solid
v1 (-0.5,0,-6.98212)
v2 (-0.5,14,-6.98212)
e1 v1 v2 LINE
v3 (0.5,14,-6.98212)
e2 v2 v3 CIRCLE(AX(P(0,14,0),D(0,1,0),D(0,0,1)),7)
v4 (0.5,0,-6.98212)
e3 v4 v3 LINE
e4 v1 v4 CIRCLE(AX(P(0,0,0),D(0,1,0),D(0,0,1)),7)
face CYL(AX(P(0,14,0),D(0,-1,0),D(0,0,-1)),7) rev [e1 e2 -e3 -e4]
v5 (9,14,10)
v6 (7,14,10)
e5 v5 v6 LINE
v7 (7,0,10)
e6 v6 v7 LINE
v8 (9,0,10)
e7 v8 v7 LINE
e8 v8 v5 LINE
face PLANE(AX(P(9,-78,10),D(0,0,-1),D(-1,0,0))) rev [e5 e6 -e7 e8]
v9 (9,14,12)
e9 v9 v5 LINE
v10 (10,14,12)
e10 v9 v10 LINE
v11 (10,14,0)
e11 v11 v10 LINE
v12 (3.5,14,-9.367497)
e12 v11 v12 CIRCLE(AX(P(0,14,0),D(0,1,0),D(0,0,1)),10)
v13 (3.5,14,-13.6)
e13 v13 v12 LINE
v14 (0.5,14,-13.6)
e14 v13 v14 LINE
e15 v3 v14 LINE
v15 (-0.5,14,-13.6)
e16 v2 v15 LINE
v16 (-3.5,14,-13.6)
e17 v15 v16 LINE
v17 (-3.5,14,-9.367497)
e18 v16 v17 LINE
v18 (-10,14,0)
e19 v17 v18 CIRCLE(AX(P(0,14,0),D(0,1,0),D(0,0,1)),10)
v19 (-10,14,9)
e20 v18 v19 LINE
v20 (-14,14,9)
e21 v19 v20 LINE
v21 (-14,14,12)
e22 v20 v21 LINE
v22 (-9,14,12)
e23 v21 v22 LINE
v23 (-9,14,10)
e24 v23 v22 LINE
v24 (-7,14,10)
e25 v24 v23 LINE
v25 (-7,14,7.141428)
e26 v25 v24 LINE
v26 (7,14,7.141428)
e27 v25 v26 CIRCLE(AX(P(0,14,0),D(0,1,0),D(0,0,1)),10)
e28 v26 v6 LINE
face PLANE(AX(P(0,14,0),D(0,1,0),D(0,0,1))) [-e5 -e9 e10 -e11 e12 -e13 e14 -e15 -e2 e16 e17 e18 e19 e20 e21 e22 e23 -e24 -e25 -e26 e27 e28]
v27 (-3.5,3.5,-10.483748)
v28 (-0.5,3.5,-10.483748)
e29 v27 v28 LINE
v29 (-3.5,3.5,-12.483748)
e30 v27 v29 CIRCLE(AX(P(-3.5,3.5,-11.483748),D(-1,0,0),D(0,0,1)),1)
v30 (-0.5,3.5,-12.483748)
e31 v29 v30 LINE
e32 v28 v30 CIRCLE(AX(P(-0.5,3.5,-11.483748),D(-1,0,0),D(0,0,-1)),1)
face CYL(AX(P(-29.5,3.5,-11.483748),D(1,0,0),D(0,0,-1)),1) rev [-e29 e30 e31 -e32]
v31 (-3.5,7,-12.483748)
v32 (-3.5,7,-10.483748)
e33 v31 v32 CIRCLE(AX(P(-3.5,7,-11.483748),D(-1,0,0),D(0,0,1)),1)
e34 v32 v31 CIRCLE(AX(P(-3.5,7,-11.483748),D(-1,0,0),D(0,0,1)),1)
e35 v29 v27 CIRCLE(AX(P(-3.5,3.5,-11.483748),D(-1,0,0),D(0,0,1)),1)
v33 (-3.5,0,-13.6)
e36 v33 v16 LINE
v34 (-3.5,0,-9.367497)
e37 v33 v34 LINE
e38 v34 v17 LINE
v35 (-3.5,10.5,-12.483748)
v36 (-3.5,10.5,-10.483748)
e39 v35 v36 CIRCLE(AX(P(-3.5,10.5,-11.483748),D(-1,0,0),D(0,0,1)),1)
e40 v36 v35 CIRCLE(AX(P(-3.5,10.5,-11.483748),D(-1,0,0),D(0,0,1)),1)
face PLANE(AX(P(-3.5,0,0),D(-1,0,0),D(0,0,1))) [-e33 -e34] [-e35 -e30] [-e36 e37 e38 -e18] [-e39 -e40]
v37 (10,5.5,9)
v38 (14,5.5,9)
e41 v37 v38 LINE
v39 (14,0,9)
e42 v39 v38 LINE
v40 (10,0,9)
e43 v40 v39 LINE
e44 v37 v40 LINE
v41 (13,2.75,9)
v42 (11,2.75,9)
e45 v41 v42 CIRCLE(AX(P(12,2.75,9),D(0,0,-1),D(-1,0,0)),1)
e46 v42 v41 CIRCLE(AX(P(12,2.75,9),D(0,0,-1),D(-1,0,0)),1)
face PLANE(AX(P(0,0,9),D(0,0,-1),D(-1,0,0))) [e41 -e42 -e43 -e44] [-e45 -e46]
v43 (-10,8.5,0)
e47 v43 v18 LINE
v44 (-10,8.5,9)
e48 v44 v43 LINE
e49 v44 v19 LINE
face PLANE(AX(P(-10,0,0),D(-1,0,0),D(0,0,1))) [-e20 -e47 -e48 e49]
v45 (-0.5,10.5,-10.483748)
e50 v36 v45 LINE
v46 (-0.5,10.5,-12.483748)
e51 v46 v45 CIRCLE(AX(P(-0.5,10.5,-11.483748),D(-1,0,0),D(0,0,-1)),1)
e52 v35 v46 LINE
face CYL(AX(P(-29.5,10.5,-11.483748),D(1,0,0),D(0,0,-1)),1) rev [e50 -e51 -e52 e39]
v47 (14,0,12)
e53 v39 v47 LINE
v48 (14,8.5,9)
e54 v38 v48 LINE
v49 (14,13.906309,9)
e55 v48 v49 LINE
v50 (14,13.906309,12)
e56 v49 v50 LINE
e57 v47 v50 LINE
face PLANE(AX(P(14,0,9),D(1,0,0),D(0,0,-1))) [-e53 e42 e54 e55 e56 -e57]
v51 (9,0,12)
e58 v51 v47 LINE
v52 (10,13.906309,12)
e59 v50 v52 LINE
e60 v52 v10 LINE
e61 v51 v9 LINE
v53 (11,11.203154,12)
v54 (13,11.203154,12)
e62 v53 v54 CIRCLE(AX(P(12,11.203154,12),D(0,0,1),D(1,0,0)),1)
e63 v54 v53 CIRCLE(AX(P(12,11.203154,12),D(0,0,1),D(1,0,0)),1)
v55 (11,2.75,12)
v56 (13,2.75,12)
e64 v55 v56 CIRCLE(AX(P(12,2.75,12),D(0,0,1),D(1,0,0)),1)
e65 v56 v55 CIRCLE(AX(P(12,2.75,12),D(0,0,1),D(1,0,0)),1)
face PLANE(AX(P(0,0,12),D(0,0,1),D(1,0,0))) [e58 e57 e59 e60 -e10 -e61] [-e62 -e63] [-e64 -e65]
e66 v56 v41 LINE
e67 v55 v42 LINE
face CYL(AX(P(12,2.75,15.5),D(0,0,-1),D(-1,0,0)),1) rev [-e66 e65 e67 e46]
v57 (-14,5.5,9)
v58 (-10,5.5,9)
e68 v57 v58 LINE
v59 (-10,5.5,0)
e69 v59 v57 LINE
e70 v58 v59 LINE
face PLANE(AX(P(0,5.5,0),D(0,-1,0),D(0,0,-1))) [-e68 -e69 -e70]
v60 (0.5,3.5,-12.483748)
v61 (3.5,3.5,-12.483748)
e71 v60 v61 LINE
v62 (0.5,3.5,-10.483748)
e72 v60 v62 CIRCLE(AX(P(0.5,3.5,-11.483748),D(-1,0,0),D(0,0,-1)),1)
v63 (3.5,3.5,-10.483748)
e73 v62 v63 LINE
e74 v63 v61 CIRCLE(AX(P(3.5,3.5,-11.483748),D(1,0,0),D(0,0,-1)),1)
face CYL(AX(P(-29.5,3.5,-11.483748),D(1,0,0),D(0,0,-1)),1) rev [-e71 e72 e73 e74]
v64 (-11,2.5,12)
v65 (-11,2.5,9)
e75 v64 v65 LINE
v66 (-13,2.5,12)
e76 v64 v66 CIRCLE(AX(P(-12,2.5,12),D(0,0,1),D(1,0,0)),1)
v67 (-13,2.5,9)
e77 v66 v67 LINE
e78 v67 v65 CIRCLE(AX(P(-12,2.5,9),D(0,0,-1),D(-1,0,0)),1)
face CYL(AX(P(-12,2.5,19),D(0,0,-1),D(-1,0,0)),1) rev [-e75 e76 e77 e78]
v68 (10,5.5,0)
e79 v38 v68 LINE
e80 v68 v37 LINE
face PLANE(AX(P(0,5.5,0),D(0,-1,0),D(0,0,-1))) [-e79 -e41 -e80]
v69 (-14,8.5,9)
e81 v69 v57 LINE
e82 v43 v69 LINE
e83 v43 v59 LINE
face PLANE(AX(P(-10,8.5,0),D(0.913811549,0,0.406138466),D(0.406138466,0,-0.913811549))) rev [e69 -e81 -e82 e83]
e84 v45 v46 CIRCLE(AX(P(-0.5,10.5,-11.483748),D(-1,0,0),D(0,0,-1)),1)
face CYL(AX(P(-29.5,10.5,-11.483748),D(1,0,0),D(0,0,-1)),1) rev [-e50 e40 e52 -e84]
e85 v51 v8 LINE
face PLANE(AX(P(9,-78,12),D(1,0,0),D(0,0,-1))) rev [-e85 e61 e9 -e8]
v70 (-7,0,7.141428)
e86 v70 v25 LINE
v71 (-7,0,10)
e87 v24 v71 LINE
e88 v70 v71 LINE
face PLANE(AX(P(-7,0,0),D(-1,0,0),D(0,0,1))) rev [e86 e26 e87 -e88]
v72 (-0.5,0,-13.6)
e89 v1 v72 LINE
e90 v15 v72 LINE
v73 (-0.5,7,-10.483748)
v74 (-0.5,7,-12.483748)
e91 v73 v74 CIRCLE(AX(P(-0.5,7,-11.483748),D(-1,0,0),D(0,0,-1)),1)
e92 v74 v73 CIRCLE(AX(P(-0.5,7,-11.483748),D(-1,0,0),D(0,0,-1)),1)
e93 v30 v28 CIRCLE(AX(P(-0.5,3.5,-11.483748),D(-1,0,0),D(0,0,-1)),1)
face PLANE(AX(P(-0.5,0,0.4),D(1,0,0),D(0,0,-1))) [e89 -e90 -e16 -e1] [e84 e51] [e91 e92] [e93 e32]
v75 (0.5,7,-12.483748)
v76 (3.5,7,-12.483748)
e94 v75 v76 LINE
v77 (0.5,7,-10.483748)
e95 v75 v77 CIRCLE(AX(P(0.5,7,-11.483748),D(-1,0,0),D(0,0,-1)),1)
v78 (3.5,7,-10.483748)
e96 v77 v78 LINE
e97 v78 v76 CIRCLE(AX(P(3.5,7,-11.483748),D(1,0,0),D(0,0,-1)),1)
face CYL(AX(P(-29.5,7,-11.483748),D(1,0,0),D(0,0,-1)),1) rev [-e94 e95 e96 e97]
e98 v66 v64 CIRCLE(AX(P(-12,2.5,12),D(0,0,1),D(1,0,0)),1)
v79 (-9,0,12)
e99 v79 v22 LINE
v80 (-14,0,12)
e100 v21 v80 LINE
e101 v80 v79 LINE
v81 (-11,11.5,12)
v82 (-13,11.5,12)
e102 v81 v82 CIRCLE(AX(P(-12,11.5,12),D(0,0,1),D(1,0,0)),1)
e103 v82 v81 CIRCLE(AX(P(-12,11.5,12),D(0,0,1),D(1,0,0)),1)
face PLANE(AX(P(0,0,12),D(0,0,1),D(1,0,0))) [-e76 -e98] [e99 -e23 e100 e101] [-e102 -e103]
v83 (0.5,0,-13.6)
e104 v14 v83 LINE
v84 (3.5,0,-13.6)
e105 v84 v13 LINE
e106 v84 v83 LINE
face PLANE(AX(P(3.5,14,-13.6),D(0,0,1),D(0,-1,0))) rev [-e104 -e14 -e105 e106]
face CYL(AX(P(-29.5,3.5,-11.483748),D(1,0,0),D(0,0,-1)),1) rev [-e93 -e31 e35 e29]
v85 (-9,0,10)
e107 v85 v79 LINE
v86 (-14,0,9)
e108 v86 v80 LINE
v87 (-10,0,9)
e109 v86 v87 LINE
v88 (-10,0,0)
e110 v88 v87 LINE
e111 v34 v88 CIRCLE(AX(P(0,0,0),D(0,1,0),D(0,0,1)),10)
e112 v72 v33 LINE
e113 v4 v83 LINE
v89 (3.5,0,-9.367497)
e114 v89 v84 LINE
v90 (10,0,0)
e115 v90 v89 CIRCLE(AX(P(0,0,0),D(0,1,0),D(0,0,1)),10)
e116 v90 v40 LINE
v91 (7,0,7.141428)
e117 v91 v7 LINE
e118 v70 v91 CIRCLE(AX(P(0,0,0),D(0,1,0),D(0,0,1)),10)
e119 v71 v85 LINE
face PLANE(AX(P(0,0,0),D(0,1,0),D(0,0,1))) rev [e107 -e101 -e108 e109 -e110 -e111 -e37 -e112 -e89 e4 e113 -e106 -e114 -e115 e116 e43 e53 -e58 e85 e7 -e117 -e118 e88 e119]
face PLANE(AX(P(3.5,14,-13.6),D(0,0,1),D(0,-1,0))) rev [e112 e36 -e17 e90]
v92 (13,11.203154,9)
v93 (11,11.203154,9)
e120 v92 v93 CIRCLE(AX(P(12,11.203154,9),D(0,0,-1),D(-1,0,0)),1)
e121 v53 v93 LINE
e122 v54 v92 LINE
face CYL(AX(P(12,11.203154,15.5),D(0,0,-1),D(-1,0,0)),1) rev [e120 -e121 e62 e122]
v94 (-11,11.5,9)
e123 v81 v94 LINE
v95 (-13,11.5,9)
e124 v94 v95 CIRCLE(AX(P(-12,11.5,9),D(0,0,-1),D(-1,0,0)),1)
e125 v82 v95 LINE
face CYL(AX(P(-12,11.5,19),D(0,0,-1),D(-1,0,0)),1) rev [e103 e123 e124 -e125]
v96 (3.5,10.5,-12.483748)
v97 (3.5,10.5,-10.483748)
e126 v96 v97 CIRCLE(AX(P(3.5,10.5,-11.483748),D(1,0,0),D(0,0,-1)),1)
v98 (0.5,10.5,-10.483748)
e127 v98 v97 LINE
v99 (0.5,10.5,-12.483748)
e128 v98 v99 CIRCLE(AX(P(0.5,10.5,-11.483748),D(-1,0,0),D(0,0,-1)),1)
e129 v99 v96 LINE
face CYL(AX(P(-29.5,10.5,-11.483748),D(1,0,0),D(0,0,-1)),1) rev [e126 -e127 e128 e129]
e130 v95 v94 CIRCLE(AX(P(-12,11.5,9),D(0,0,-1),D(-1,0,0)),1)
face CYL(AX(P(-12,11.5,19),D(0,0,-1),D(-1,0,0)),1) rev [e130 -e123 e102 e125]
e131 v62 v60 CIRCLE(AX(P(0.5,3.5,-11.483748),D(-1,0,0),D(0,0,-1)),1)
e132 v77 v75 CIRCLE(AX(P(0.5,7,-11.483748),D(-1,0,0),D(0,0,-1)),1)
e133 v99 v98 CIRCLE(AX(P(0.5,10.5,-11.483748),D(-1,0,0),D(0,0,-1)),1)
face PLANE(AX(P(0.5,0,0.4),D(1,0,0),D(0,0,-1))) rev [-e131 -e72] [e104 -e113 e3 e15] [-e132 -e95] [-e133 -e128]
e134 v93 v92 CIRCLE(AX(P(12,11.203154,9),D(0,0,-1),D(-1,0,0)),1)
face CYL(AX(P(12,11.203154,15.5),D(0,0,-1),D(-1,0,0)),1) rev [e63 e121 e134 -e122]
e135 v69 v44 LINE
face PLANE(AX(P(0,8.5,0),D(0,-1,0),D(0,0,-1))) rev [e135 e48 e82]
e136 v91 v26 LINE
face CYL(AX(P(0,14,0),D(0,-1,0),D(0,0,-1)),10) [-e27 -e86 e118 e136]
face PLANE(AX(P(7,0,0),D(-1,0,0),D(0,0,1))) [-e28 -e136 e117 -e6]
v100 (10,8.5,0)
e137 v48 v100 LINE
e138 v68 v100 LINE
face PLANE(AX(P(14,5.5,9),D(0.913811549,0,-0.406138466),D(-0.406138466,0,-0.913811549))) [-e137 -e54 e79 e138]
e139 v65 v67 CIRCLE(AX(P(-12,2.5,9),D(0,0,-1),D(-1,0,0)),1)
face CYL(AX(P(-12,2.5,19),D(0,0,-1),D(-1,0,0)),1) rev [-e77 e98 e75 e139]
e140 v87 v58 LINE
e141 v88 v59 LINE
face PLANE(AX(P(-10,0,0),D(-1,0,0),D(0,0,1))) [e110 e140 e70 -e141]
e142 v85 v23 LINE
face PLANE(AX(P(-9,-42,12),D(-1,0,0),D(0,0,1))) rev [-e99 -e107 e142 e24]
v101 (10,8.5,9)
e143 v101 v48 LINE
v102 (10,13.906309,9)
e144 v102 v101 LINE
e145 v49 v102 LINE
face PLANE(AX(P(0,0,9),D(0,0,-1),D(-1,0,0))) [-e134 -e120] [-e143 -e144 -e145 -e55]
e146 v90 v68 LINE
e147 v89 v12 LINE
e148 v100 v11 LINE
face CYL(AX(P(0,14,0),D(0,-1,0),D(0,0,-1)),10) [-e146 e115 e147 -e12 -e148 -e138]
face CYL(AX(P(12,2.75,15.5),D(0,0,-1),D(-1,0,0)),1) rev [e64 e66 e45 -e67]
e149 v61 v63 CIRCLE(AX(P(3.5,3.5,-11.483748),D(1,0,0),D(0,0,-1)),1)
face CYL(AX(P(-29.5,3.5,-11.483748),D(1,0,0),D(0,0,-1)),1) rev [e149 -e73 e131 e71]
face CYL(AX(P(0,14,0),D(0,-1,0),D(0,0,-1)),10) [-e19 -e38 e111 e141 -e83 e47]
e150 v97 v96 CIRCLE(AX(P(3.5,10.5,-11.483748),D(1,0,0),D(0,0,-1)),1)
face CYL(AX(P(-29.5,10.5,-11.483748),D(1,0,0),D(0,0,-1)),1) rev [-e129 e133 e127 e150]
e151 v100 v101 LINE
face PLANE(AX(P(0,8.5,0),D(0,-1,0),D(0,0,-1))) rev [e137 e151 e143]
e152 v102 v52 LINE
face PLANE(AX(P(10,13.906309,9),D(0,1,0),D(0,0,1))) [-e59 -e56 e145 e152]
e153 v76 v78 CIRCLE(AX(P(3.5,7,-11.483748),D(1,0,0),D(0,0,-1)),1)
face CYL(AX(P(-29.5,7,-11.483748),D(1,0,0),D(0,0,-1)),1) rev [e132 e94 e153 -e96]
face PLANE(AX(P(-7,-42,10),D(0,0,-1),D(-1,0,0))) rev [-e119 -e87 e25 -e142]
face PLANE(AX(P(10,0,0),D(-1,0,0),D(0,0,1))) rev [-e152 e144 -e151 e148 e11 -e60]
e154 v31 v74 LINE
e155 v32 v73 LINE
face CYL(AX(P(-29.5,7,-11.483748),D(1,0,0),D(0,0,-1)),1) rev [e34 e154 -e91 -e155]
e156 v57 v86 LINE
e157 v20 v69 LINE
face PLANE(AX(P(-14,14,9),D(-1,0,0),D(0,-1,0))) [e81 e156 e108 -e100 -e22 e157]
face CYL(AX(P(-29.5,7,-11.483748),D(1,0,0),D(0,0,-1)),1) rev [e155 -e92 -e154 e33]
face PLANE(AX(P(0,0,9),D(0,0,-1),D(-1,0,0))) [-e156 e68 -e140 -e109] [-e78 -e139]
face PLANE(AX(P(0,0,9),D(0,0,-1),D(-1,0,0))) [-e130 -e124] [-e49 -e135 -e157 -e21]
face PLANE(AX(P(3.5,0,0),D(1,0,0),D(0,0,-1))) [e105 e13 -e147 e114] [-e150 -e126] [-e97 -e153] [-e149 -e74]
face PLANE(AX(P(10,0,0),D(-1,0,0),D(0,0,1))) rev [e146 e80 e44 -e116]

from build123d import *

# Parameters (mm, degrees)
BASE_BLOCK_SKETCH_R              = 10
BASE_BLOCK_SKETCH_R_2            = 7
BASE_BLOCK_DEPTH                 = 14
CLAMP_START                      = -14
CLAMP_RING_DEPTH                 = 14
SIDE_RIB_SKETCH_W                = 3.6
SIDE_RIB_SKETCH_H                = 14
SIDE_RIB_DEPTH                   = 3.5
RIB_START                        = -14
RIB_INFILL_DEPTH                 = 14
MOUNTING_EAR_A_SKETCH_W          = 4
MOUNTING_EAR_A_SKETCH_H          = 13.906308923
MOUNTING_EAR_A_DEPTH             = 3
MOUNTING_EAR_B_SKETCH_W          = 4
MOUNTING_EAR_B_SKETCH_H          = 14
MOUNTING_EAR_B_DEPTH             = 3
CLAMP_SLIT_A_SKETCH_W            = 2
CLAMP_SLIT_A_SKETCH_H            = 2
CLAMP_SLIT_A_DEPTH               = 56
CLAMP_SLIT_B_SKETCH_W            = 2
CLAMP_SLIT_B_SKETCH_H            = 2
CLAMP_SLIT_B_DEPTH               = 92
TRIANGULAR_RELIEF_CUT_DEPTH      = 54
TRIANGULAR_RELIEF_CUT_DEPTH_BACK = 33
TRIANGULAR_RELIEF_SKETCH_R       = 1
RIB_GROOVE_SKETCH_W              = 0.5
RIB_GROOVE_SKETCH_H              = 14
RIB_GROOVE_CUT_DEPTH             = 14
EAR_A_GUSSET_DEPTH               = 1.5
EAR_A_HOLES_SKETCH_R             = 1
EAR_A_HOLES_2X_2_DEPTH           = 6.5
EAR_B_GUSSET_DEPTH               = 1.5
EAR_B_HOLES_SKETCH_R             = 1
EAR_B_HOLES_2X_2_DEPTH           = 10


with BuildPart() as part:
    # Base Block Sketch → Base Block (new body)
    with BuildSketch(Plane(origin=(0, 0, 0), x_dir=(1, 0, 0), z_dir=(0, 1, 0))):
        with Locations(Location((0, 0, 0), (0, 0, 270))):
            Circle(BASE_BLOCK_SKETCH_R)
        with Locations(Location((0, 0, 0), (0, 0, 270))):
            Circle(BASE_BLOCK_SKETCH_R_2, mode=Mode.SUBTRACT)
    extrude(amount=BASE_BLOCK_DEPTH)

    # Clamp Ring Sketch → Clamp Ring (add)
    with BuildSketch(Plane(origin=(0, 14, 0), x_dir=(1, 0, 0), z_dir=(0, 1, 0)).offset(CLAMP_START)):
        with BuildLine():
            Line((-7, -12), (-7, -7.141428429))
            ThreePointArc((-7, -7.141428429), (-9.219544457, -3.872983346), (-10, 0))
            Line((-10, 0), (-10, -12))
            Line((-10, -12), (-7, -12))
        make_face()
        with BuildLine():
            Line((10, -12), (10, 0))
            ThreePointArc((10, 0), (9.219544457, -3.872983346), (7, -7.141428429))
            Line((7, -7.141428429), (7, -12))
            Line((7, -12), (10, -12))
        make_face()
    extrude(amount=CLAMP_RING_DEPTH)



with BuildPart() as body_2:
    # Side Rib Sketch → Side Rib (new, symmetric)
    with BuildSketch(Plane(origin=(0, 0, 0), x_dir=(0, 0, -1), z_dir=(1, 0, 0))):
        with Locations((11.8, 7)):
            Rectangle(SIDE_RIB_SKETCH_W, SIDE_RIB_SKETCH_H)
    extrude(amount=SIDE_RIB_DEPTH, both=True)


with BuildPart() as part_1:
    add(part.part)

    add(body_2.part)  # Rib Infill merges body 2
    # Rib Infill Sketch → Rib Infill (add)
    with BuildSketch(Plane(origin=(0, 14, 0), x_dir=(1, 0, 0), z_dir=(0, 1, 0)).offset(RIB_START)):
        with BuildLine():
            Line((0, 10), (-3.5, 10))
            Line((-3.5, 10), (-3.5, 9.367496998))
            ThreePointArc((-3.5, 9.367496998), (-1.778346145, 9.840603893), (0, 10))
        make_face()
        with BuildLine():
            Line((3.5, 10), (0, 10))
            ThreePointArc((0, 10), (1.778346145, 9.840603893), (3.5, 9.367496998))
            Line((3.5, 9.367496998), (3.5, 10))
        make_face()
    extrude(amount=RIB_INFILL_DEPTH)

    # Mounting Ear A Sketch → Mounting Ear A (add)
    with BuildSketch(Plane.XY.offset(12)):
        with Locations((12, 6.953154462)):
            Rectangle(MOUNTING_EAR_A_SKETCH_W, MOUNTING_EAR_A_SKETCH_H)
    extrude(amount=-MOUNTING_EAR_A_DEPTH)

    # Mounting Ear B Sketch → Mounting Ear B (add)
    with BuildSketch(Plane.XY.offset(12)):
        with Locations((-12, 7)):
            Rectangle(MOUNTING_EAR_B_SKETCH_W, MOUNTING_EAR_B_SKETCH_H)
    extrude(amount=-MOUNTING_EAR_B_DEPTH)

    # Clamp Slit A Sketch → Clamp Slit A (cut)
    with BuildSketch(Plane(origin=(0, 14, 0), x_dir=(1, 0, 0), z_dir=(0, 1, 0))):
        with Locations((-8, -11)):
            Rectangle(CLAMP_SLIT_A_SKETCH_W, CLAMP_SLIT_A_SKETCH_H)
    extrude(amount=-CLAMP_SLIT_A_DEPTH, mode=Mode.SUBTRACT)

    # Clamp Slit B Sketch → Clamp Slit B (cut)
    with BuildSketch(Plane(origin=(0, 14, 0), x_dir=(1, 0, 0), z_dir=(0, 1, 0))):
        with Locations((8, -11)):
            Rectangle(CLAMP_SLIT_B_SKETCH_W, CLAMP_SLIT_B_SKETCH_H)
    extrude(amount=-CLAMP_SLIT_B_DEPTH, mode=Mode.SUBTRACT)

    # Triangular Relief Sketch → Triangular Relief Cut (cut, two sides: drawn at the far end of the back side and taken through both)
    with BuildSketch(Plane(origin=(3.5, 0, 0), x_dir=(0, 0, -1), z_dir=(1, 0, 0)).offset(-TRIANGULAR_RELIEF_CUT_DEPTH_BACK)):
        with Locations((11.483748499, 7)):
            Circle(TRIANGULAR_RELIEF_SKETCH_R)
        with Locations((11.483748499, 3.5)):
            Circle(TRIANGULAR_RELIEF_SKETCH_R)
        with Locations((11.483748499, 10.5)):
            Circle(TRIANGULAR_RELIEF_SKETCH_R)
    extrude(amount=TRIANGULAR_RELIEF_CUT_DEPTH + TRIANGULAR_RELIEF_CUT_DEPTH_BACK, mode=Mode.SUBTRACT)

    # Rib Groove Sketch → Rib Groove Cut (cut)
    with BuildSketch(Plane(origin=(0, 0, -13.6), x_dir=(-1, 0, 0), z_dir=(0, 0, -1))):
        with Locations((0.25, 7)):
            Rectangle(RIB_GROOVE_SKETCH_W, RIB_GROOVE_SKETCH_H)
        with Locations((-0.25, 7)):
            Rectangle(RIB_GROOVE_SKETCH_W, RIB_GROOVE_SKETCH_H)
    extrude(amount=-RIB_GROOVE_CUT_DEPTH, mode=Mode.SUBTRACT)

    # Ear A Gusset Sketch → Ear A Gusset (add, symmetric)
    with BuildSketch(Plane(origin=(0, 7, 0), x_dir=(1, 0, 0), z_dir=(0, 1, 0))):
        Polygon((14, -9), (10, 0), (10, -9), align=None)
    extrude(amount=EAR_A_GUSSET_DEPTH, both=True)

    # Ear A Holes Sketch → Ear A Holes 2xØ2 (cut, symmetric)
    with BuildSketch(Plane(origin=(0, 0, 9), x_dir=(-1, 0, 0), z_dir=(0, 0, -1))):
        with Locations((-12, 11.203154462)):
            Circle(EAR_A_HOLES_SKETCH_R)
        with Locations((-12, 2.75)):
            Circle(EAR_A_HOLES_SKETCH_R)
    extrude(amount=EAR_A_HOLES_2X_2_DEPTH, both=True, mode=Mode.SUBTRACT)

    # Ear B Gusset Sketch → Ear B Gusset (add, symmetric)
    with BuildSketch(Plane(origin=(0, 7, 0), x_dir=(1, 0, 0), z_dir=(0, 1, 0))):
        Polygon((-10, 0), (-14, -9), (-10, -9), align=None)
    extrude(amount=EAR_B_GUSSET_DEPTH, both=True)

    # Ear B Holes Sketch → Ear B Holes 2xØ2 (cut, symmetric)
    with BuildSketch(Plane(origin=(0, 0, 9), x_dir=(-1, 0, 0), z_dir=(0, 0, -1))):
        with Locations((12, 2.5)):
            Circle(EAR_B_HOLES_SKETCH_R)
        with Locations((12, 11.5)):
            Circle(EAR_B_HOLES_SKETCH_R)
    extrude(amount=EAR_B_HOLES_2X_2_DEPTH, both=True, mode=Mode.SUBTRACT)


solid = part_1.part
